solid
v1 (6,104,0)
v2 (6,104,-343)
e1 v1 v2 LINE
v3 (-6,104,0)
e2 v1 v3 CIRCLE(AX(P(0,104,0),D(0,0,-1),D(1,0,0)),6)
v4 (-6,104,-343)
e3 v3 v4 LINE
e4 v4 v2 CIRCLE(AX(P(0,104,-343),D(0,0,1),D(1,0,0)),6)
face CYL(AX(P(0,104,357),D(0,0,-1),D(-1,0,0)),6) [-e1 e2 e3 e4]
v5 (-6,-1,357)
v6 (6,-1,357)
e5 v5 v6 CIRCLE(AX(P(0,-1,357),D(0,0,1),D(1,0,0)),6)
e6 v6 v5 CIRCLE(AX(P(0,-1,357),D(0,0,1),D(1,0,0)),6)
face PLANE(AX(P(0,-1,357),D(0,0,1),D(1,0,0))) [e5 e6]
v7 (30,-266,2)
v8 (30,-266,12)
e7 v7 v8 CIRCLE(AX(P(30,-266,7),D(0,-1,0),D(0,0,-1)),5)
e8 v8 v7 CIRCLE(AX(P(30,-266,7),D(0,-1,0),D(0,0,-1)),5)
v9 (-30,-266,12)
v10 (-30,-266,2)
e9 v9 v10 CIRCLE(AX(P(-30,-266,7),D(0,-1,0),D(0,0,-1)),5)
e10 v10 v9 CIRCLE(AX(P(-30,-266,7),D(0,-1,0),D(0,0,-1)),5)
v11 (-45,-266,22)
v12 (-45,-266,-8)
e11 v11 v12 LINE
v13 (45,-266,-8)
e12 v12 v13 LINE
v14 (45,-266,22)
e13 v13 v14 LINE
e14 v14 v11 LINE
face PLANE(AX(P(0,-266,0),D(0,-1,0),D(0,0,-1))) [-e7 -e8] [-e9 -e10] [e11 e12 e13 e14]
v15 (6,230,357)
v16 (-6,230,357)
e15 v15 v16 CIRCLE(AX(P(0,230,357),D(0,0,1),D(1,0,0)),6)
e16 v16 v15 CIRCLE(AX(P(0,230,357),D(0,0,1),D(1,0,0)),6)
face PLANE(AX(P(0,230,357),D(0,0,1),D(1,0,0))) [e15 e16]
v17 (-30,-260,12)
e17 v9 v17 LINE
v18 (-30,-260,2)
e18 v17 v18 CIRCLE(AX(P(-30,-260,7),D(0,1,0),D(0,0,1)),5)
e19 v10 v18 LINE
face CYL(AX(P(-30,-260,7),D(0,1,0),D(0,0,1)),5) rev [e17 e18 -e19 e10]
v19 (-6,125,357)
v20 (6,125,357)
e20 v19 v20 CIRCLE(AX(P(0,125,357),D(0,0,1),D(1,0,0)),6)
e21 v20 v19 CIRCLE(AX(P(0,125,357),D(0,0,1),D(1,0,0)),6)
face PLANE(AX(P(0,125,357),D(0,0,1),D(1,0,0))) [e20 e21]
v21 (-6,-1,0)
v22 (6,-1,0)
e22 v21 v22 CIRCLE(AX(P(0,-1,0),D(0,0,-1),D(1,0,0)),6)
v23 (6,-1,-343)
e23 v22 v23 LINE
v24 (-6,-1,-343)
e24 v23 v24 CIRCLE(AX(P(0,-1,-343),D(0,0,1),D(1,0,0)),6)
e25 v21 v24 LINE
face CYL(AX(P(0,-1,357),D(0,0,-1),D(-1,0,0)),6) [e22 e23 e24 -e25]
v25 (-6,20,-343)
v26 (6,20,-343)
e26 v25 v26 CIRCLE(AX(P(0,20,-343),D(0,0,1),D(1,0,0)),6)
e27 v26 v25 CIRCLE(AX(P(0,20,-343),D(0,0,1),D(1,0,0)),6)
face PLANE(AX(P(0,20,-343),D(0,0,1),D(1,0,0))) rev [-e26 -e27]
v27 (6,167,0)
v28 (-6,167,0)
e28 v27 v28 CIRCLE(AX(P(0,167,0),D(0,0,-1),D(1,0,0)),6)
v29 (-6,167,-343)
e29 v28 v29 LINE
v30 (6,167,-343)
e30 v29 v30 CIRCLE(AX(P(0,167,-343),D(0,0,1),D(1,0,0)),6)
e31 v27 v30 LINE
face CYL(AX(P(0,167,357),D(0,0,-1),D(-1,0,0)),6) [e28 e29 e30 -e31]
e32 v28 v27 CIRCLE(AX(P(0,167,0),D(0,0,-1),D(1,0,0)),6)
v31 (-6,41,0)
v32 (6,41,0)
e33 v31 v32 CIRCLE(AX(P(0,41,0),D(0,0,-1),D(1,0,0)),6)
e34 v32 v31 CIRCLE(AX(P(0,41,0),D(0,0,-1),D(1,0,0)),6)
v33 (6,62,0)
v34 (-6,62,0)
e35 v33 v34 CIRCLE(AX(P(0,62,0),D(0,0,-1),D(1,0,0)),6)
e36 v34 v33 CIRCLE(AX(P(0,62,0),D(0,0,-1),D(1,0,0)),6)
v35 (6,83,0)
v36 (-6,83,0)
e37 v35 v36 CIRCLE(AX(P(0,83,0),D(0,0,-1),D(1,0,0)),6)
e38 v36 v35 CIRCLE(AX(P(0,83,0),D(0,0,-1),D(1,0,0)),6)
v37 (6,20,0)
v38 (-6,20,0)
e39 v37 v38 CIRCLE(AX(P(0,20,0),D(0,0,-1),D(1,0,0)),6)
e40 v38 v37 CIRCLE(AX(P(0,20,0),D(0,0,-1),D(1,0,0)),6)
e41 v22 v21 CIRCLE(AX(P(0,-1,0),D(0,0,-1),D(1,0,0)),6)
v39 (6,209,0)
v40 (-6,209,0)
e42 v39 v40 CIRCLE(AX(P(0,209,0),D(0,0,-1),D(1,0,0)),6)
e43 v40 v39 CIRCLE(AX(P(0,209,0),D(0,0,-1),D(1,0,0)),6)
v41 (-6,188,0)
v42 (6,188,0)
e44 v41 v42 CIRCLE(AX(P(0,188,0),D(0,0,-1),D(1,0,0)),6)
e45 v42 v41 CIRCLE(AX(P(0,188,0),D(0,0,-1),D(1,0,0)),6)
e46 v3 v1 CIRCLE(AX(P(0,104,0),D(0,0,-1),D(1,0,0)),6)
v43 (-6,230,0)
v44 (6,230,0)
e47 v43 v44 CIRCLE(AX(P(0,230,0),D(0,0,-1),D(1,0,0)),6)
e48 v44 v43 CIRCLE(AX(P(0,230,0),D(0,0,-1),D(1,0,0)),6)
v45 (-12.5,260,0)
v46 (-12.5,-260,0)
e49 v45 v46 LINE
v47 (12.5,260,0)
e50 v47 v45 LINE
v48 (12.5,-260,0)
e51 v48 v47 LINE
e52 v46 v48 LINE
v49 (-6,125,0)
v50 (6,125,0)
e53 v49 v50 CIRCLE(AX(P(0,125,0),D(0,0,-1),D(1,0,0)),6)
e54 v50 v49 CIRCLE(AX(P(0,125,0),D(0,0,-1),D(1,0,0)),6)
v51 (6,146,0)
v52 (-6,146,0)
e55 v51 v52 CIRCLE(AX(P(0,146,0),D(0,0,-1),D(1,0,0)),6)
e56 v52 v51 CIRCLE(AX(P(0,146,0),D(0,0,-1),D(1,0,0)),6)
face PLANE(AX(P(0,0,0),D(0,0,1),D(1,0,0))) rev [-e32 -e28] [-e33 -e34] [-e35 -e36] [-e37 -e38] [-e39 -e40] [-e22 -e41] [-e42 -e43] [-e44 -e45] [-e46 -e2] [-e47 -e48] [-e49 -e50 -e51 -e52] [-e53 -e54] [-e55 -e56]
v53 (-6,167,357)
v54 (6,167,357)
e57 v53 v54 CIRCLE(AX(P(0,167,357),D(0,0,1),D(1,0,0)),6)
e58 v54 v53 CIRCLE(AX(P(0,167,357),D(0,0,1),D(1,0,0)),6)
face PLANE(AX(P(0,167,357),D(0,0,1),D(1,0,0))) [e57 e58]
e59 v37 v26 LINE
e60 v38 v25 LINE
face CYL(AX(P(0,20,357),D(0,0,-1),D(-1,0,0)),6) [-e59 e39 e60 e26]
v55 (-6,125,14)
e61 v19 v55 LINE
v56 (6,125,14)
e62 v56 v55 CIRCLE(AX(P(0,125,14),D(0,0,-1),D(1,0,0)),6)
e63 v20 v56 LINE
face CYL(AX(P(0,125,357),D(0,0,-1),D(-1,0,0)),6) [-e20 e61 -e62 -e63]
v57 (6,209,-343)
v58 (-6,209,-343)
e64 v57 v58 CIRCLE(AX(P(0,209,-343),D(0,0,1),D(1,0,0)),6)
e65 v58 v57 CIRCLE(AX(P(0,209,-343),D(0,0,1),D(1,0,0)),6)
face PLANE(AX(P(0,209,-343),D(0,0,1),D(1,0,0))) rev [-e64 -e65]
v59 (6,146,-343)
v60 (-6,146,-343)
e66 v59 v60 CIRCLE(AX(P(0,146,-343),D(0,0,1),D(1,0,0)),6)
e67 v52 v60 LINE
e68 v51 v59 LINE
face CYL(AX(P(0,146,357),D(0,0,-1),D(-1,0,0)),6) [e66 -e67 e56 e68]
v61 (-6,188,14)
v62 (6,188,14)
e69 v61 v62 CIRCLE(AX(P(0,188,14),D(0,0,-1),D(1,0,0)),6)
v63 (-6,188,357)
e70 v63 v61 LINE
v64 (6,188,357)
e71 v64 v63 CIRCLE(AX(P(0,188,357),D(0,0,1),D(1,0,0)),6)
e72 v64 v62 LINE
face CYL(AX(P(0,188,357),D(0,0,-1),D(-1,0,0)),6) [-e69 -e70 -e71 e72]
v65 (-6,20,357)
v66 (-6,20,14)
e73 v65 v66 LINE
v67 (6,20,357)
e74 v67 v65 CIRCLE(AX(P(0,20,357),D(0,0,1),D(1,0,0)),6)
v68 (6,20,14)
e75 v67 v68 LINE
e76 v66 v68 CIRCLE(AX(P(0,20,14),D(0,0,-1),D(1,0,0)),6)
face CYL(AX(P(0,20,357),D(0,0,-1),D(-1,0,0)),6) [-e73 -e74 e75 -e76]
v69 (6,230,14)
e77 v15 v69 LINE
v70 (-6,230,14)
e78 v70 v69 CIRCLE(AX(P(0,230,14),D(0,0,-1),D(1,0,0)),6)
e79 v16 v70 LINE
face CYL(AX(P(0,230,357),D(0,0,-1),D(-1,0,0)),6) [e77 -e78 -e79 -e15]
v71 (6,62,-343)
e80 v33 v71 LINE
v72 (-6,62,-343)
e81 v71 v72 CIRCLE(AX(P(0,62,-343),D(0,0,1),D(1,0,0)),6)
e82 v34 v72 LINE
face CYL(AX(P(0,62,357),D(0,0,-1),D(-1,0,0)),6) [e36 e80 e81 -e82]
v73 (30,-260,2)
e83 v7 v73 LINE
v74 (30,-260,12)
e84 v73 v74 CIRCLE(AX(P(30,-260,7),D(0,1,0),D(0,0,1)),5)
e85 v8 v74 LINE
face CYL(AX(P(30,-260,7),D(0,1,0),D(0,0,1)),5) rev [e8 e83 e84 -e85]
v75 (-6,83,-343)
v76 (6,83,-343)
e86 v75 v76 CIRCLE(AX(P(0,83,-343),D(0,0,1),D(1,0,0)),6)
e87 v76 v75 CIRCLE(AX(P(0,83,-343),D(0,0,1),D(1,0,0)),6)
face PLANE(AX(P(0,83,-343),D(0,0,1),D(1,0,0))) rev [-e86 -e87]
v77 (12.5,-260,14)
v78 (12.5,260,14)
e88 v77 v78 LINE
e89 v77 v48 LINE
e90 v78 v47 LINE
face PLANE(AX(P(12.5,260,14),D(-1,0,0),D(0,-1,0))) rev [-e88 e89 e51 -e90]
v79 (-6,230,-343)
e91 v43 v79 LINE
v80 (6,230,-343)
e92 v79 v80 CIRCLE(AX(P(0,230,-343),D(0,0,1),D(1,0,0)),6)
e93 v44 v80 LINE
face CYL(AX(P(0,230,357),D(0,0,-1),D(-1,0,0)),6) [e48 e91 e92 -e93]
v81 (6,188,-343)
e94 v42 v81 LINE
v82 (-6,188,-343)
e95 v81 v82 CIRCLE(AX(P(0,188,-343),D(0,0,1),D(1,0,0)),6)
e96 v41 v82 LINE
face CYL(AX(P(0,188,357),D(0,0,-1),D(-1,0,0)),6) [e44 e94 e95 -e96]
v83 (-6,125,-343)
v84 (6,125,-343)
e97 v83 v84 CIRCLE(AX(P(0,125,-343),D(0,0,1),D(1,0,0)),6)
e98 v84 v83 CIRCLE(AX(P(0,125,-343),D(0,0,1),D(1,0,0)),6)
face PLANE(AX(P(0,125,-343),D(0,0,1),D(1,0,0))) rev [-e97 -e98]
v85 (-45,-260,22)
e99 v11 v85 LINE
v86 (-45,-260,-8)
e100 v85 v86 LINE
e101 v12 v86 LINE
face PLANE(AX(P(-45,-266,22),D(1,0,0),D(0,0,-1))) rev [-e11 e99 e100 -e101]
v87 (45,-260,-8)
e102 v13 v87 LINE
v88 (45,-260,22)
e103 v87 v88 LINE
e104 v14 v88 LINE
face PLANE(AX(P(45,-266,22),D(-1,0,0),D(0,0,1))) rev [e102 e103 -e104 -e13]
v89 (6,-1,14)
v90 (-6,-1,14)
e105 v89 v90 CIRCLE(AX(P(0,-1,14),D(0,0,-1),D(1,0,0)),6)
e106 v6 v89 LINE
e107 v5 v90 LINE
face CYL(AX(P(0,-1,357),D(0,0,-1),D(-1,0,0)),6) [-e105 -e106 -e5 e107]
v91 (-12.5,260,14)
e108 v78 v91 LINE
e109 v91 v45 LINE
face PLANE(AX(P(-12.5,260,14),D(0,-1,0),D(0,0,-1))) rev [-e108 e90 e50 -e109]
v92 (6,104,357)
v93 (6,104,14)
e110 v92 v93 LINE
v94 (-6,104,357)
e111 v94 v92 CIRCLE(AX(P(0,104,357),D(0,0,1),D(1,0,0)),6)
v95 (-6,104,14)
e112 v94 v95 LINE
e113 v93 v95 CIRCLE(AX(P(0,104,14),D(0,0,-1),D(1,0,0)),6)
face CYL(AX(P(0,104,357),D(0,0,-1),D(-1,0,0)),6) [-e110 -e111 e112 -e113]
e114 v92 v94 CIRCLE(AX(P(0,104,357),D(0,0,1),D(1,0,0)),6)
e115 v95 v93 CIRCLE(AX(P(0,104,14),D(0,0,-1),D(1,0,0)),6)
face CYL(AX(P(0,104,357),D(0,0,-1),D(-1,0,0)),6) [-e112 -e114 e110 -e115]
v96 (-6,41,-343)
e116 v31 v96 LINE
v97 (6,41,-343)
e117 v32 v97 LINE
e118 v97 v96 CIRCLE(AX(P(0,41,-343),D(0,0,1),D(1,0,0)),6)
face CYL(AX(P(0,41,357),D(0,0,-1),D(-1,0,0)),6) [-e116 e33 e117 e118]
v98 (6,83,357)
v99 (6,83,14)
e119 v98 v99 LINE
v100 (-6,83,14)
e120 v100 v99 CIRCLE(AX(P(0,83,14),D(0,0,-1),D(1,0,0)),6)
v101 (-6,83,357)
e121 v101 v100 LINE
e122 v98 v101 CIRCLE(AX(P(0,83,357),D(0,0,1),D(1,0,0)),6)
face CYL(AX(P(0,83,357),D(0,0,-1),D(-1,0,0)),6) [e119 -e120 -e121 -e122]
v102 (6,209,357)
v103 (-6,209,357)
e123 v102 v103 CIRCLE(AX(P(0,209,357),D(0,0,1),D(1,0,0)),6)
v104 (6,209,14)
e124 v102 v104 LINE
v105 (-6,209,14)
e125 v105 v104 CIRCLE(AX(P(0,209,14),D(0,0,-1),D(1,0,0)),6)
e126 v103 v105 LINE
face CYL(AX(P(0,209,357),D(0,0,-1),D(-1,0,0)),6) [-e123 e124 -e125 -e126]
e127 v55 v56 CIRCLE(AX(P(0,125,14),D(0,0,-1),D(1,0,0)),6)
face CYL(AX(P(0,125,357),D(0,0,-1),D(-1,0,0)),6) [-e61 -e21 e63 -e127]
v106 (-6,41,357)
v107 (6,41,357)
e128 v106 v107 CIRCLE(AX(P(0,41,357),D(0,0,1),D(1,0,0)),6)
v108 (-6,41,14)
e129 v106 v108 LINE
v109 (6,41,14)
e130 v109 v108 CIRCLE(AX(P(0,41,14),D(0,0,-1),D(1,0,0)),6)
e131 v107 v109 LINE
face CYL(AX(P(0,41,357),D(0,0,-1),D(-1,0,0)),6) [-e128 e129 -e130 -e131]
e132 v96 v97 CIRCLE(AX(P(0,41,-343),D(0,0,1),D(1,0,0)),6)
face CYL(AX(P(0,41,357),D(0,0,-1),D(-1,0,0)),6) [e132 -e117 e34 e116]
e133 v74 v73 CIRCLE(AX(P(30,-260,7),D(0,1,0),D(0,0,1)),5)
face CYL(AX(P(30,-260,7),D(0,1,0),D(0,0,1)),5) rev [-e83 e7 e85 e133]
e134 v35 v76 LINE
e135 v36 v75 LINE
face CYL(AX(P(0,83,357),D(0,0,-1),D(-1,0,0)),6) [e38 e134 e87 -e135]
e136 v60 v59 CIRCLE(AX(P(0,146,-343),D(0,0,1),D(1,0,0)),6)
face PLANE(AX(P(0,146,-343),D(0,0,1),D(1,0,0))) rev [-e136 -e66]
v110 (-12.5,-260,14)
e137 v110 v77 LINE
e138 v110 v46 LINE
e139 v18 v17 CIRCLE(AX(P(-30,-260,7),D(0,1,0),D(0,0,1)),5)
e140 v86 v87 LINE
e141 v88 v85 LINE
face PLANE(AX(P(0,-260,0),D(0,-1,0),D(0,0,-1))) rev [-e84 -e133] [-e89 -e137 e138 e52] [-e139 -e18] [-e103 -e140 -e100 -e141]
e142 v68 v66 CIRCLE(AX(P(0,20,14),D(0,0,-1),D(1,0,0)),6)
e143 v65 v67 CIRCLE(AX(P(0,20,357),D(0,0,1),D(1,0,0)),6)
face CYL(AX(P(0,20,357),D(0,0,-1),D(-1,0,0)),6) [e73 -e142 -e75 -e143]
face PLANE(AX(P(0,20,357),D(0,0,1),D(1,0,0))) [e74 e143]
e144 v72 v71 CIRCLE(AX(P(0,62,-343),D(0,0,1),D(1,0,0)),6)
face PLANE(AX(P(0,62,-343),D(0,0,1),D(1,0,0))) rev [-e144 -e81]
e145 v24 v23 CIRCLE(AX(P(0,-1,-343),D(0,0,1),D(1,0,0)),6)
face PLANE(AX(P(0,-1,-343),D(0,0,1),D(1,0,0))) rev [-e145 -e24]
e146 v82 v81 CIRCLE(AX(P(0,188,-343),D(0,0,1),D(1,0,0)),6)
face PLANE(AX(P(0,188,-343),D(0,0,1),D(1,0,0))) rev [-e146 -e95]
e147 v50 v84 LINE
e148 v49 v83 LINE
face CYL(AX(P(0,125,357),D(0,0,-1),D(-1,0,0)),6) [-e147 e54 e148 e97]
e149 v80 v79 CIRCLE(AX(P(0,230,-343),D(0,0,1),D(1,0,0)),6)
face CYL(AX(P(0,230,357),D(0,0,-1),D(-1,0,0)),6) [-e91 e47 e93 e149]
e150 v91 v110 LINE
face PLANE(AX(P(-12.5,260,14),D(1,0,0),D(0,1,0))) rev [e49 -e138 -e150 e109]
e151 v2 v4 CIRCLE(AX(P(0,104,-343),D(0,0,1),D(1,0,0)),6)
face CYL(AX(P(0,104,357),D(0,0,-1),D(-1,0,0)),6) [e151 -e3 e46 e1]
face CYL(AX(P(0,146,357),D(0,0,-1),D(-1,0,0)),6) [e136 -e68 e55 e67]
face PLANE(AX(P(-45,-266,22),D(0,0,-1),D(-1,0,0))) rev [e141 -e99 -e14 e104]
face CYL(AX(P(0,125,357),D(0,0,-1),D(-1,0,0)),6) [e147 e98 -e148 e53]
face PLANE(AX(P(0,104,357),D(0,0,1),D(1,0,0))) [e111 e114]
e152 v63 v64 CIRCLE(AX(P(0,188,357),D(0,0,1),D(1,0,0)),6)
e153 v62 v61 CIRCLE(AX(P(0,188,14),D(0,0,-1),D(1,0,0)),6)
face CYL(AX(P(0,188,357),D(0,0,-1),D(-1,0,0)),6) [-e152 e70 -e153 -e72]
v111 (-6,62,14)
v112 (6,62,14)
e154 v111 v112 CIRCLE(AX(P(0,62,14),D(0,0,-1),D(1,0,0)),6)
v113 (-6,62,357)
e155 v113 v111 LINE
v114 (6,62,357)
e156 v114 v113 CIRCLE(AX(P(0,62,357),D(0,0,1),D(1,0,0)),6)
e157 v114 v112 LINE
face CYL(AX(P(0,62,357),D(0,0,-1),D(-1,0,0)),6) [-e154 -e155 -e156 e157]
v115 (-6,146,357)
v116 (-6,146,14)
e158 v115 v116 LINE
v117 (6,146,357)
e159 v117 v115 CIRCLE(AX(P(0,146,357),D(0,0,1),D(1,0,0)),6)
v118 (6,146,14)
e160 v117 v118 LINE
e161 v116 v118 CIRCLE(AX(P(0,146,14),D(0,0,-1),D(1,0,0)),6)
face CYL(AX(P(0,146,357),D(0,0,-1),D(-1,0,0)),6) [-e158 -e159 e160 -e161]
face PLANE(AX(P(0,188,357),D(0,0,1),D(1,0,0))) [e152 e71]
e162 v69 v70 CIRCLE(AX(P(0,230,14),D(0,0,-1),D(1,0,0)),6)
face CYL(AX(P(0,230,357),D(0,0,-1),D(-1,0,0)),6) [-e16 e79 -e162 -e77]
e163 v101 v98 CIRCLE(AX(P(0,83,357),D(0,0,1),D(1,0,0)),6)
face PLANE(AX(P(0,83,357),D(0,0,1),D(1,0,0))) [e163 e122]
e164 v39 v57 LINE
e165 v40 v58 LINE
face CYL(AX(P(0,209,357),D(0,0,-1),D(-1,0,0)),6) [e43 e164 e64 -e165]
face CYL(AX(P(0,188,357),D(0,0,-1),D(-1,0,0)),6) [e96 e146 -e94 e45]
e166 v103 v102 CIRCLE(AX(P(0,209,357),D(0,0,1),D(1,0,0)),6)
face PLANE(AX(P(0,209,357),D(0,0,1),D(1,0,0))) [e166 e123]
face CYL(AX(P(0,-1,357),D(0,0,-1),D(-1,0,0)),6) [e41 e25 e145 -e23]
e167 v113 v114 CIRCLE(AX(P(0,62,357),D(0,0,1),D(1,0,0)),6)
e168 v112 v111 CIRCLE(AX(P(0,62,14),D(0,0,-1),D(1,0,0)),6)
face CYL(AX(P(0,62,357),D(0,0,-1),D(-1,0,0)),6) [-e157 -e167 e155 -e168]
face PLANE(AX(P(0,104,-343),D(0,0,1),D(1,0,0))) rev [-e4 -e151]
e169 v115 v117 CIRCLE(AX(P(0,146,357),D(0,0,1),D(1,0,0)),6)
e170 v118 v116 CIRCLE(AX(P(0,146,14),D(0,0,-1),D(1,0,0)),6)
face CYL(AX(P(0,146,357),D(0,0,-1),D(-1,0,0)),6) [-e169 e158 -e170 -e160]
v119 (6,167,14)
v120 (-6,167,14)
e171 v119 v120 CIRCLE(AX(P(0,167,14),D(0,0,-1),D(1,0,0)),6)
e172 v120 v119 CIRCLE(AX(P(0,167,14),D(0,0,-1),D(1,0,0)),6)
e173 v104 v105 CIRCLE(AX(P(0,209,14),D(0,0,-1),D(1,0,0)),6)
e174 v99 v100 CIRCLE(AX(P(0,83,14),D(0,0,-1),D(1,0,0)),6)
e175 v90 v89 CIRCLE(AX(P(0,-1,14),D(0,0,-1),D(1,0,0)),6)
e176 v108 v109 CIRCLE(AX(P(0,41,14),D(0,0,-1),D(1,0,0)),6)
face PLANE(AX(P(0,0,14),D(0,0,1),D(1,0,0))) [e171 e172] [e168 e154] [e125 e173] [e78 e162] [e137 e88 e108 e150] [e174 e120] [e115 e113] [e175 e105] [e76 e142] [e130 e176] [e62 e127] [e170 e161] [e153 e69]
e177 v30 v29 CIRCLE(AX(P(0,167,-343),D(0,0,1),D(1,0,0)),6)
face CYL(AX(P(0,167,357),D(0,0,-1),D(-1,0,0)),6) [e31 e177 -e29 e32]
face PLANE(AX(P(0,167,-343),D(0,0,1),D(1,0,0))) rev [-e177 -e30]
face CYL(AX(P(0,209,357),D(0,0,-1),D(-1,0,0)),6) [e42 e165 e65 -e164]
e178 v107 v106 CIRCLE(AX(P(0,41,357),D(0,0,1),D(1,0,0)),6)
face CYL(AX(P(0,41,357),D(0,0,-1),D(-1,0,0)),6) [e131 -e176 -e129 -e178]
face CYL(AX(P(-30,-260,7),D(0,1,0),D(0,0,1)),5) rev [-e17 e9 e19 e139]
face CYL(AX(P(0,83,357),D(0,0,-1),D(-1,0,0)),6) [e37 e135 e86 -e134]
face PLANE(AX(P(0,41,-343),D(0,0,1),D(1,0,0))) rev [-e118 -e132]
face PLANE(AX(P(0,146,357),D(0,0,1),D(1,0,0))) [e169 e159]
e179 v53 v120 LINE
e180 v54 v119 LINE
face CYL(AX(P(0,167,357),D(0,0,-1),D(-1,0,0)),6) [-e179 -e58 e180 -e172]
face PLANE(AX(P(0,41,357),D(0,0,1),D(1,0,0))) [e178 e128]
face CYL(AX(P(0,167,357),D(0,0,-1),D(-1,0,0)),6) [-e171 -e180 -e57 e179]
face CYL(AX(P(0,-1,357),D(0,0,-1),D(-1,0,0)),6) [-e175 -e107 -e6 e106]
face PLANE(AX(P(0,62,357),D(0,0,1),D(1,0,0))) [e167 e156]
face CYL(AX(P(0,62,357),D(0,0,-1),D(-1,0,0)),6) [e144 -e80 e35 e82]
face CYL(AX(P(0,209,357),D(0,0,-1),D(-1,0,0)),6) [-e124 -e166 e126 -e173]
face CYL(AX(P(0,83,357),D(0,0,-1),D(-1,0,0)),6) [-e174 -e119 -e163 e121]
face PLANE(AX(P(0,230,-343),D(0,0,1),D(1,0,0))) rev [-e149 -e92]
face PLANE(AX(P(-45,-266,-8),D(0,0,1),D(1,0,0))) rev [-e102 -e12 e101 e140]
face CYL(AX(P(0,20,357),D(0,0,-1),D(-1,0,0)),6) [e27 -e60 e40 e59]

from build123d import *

# Parameters (mm, degrees)
SKETCH1_W                = 25
SKETCH1_H                = 520
BOSS_EXTRUDE1_DEPTH      = 14
BOSS_EXTRUDE2_START      = -7
SKETCH3_R                = 6
BOSS_EXTRUDE2_DEPTH      = 350
LPATTERN1_COUNT          = 12
LPATTERN1_PITCH          = 21
SKETCH4_W                = 90
SKETCH4_H                = 30
BOSS_EXTRUDE3_DEPTH      = 6
M8_CLEARANCE_HOLE1_D     = 10
M8_CLEARANCE_HOLE1_DEPTH = 20
M8_CLEARANCE_HOLE1_TIP   = 3.004303095


with BuildPart() as part:
    # Sketch1 → Boss-Extrude1 (new body)
    with BuildSketch(Plane.XY):
        Rectangle(SKETCH1_W, SKETCH1_H)
    extrude(amount=BOSS_EXTRUDE1_DEPTH)

    # Sketch3 → Boss-Extrude2 (add, symmetric)
    with BuildSketch(Plane.XY.offset(14).offset(BOSS_EXTRUDE2_START)):
        with Locations((0, 230)):
            Circle(SKETCH3_R)
    boss_extrude2 = extrude(amount=BOSS_EXTRUDE2_DEPTH, both=True)

    # LPattern1: Boss-Extrude2 ×12
    with Locations(*[(0, -i * LPATTERN1_PITCH, 0) for i in range(1, LPATTERN1_COUNT)]):
        add(boss_extrude2)

    # Sketch4 → Boss-Extrude3 (add)
    with BuildSketch(Plane.XZ.offset(260)):
        with Locations((0, 7)):
            Rectangle(SKETCH4_W, SKETCH4_H)
    extrude(amount=BOSS_EXTRUDE3_DEPTH)

    # M8 Clearance Hole1
    with Locations(Plane(origin=(0, -260, 0), x_dir=(1, 0, 0), z_dir=(0, 1, 0))):
        with Locations((-30, -7), (30, -7)):
            Hole(M8_CLEARANCE_HOLE1_D / 2, depth=M8_CLEARANCE_HOLE1_DEPTH)
            with Locations((0, 0, -(M8_CLEARANCE_HOLE1_DEPTH + M8_CLEARANCE_HOLE1_TIP / 2))):  # 118° drill point
                Cone(0, M8_CLEARANCE_HOLE1_D / 2, M8_CLEARANCE_HOLE1_TIP, mode=Mode.SUBTRACT)


solid = part.part
